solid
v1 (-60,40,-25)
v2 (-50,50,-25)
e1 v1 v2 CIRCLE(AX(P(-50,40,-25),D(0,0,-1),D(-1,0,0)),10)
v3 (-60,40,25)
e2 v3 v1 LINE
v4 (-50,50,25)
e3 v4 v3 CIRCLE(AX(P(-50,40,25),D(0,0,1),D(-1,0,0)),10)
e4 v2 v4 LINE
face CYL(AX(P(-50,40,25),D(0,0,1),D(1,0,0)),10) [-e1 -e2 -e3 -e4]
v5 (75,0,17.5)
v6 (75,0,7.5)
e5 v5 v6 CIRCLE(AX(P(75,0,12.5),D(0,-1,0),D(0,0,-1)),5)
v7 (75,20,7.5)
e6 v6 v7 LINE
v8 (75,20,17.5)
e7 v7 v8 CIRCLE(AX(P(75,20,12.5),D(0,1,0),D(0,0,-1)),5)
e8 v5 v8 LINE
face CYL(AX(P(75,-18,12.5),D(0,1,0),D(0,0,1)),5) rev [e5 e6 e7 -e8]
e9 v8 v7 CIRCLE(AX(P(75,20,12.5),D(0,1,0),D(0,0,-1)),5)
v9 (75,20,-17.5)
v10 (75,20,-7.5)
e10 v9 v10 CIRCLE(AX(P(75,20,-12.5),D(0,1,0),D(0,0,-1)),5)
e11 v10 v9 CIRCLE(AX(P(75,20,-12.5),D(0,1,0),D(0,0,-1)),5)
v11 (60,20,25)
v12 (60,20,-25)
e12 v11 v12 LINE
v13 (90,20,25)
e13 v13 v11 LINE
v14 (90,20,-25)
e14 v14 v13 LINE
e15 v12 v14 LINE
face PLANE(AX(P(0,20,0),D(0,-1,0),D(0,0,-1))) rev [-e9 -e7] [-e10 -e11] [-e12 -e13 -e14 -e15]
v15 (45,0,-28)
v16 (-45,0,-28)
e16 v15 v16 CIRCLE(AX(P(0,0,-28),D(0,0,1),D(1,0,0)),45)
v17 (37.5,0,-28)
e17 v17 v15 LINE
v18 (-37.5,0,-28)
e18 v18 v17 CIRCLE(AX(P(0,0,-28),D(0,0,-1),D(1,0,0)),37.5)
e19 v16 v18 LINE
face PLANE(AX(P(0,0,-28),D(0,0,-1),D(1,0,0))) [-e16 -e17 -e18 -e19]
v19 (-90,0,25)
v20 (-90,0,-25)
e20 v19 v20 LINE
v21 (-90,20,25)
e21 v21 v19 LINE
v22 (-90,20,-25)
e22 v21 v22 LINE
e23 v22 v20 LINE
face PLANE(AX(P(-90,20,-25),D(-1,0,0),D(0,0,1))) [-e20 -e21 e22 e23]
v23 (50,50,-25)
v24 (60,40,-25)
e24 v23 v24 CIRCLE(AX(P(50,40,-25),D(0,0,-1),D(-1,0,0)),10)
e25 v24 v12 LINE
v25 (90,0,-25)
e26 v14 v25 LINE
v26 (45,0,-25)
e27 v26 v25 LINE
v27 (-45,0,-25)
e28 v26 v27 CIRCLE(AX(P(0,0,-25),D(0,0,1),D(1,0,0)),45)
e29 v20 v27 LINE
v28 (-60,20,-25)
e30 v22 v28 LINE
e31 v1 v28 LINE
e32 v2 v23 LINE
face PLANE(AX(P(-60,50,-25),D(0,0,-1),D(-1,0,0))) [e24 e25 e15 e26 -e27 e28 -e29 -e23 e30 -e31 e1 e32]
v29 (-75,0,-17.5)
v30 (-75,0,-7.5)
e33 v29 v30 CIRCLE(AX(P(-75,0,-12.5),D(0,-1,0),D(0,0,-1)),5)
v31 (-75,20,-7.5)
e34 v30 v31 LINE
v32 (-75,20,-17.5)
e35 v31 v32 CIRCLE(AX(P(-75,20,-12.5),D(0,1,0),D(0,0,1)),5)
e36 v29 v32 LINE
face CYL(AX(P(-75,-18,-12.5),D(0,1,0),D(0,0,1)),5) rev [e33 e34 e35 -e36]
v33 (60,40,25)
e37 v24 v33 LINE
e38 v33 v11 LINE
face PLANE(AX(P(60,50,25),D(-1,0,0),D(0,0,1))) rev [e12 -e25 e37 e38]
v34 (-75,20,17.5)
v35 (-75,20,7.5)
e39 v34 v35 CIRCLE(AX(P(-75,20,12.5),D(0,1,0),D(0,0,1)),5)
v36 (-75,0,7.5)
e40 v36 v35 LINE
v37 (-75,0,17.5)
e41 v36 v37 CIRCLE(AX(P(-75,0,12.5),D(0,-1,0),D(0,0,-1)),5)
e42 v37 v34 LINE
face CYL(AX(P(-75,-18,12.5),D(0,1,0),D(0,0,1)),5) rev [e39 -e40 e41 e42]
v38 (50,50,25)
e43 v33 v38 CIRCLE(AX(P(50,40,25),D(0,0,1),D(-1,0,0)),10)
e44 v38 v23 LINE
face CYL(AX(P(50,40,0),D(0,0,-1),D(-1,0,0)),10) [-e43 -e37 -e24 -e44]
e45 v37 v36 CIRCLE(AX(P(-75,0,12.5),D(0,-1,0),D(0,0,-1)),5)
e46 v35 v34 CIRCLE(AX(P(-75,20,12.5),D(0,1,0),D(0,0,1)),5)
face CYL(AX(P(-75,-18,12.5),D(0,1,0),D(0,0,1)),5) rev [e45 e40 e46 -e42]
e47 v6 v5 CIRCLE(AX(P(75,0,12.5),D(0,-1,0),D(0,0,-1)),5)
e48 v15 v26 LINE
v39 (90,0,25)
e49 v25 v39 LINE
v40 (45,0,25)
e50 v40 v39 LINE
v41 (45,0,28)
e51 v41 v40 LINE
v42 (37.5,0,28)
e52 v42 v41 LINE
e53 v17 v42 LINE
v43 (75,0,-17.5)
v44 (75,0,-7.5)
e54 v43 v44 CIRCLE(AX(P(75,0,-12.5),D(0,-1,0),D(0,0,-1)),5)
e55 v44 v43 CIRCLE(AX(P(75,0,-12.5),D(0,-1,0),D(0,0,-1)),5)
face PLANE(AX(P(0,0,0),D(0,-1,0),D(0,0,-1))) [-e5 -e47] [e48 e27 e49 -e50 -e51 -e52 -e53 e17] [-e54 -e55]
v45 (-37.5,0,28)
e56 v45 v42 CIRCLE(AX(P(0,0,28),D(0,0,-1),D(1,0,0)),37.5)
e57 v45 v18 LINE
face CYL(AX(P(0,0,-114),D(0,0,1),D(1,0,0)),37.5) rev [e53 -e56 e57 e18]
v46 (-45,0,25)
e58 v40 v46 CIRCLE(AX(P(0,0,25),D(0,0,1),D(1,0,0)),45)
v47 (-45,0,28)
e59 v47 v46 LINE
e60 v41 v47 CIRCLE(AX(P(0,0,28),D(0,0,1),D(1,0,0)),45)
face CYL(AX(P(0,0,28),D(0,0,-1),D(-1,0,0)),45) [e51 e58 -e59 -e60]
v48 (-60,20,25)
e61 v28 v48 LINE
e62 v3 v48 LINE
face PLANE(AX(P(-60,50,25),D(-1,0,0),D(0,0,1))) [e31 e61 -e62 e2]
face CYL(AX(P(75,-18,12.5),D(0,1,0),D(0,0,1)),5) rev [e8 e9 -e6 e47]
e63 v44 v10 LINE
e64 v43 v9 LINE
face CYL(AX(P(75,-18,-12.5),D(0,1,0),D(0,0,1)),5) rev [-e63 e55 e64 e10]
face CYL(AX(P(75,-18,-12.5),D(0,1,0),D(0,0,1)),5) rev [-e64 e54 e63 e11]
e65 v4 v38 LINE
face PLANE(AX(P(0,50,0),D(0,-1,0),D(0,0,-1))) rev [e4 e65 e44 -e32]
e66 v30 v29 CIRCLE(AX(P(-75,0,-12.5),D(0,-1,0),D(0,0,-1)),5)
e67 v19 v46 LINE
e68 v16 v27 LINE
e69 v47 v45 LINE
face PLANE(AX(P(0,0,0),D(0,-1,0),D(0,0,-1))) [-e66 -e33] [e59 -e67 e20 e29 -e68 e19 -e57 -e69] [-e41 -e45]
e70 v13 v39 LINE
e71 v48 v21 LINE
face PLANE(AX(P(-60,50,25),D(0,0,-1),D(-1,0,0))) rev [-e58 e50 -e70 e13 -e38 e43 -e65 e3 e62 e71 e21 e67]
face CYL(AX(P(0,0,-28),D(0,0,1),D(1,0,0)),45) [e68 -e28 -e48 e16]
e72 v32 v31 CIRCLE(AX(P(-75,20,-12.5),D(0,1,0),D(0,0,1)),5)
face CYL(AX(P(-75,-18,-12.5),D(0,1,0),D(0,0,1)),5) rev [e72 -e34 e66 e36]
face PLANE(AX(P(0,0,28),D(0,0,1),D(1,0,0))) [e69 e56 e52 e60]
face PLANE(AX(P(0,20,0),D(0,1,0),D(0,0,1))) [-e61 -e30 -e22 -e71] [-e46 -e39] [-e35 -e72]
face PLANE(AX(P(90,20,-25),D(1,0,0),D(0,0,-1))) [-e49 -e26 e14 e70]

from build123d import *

# Parameters (mm, degrees)
SKETCH_2_W          = 120
SKETCH_2_H          = 50
EXTRUDE_1_DEPTH     = 50
SKETCH_3_R          = 37.5
CUT_EXTRUDE_1_DEPTH = 139
FILLET_1_R          = 10
SKETCH_4_W          = 30
SKETCH_4_H          = 50
EXTRUDE_2_DEPTH     = 20
EXTRUDE_START       = 3
EXTRUDE_3_DEPTH     = 3
SKETCH_6_R          = 5
CUT_EXTRUDE_2_DEPTH = 38


with BuildPart() as part:
    # 草图2 → 凸台-拉伸1 (new body)
    with BuildSketch(Plane(origin=(0, 0, 0), x_dir=(1, 0, 0), z_dir=(0, 1, 0))):
        Rectangle(SKETCH_2_W, SKETCH_2_H)
    extrude(amount=EXTRUDE_1_DEPTH)

    # 草图3 → 切除-拉伸1 (cut)
    with BuildSketch(Plane.XY.offset(25)):
        Circle(SKETCH_3_R)
    extrude(amount=-CUT_EXTRUDE_1_DEPTH, mode=Mode.SUBTRACT)

    # 圆角1
    fillet_1_edges = [part.edges().sort_by_distance(p)[0] for p in [
        (60, 50, 0),
        (-60, 50, 0),
    ]]
    fillet(fillet_1_edges, radius=FILLET_1_R)

    # 草图4 → 凸台-拉伸2 (add)
    with BuildSketch(Plane.XZ):
        with Locations((-75, 0)):
            Rectangle(SKETCH_4_W, SKETCH_4_H)
        with Locations((75, 0)):
            Rectangle(SKETCH_4_W, SKETCH_4_H)
    extrude(amount=-EXTRUDE_2_DEPTH)

    # 草图5 → 凸台-拉伸3 (add)
    with BuildSketch(Plane.XY.offset(25).offset(EXTRUDE_START)):
        with BuildLine():
            Line((-45, 0), (-37.5, 0))
            ThreePointArc((-37.5, 0), (0, 37.5), (37.5, 0))
            Line((37.5, 0), (45, 0))
            ThreePointArc((45, 0), (0, 45), (-45, 0))
        make_face()
    extrude_3 = extrude(amount=-EXTRUDE_3_DEPTH)

    # 镜向1: 凸台-拉伸3 across plane
    add(extrude_3.mirror(Plane.XY))

    # 草图6 → 切除-拉伸2 (cut)
    with BuildSketch(Plane(origin=(0, 20, 0), x_dir=(1, 0, 0), z_dir=(0, 1, 0))):
        with Locations(Location((-75, 12.5, 0), (0, 0, 270))):
            Circle(SKETCH_6_R)
        with Locations(Location((-75, -12.5, 0), (0, 0, 270))):
            Circle(SKETCH_6_R)
        with Locations(Location((75, -12.5, 0), (0, 0, 90))):
            Circle(SKETCH_6_R)
        with Locations(Location((75, 12.5, 0), (0, 0, 90))):
            Circle(SKETCH_6_R)
    extrude(amount=-CUT_EXTRUDE_2_DEPTH, mode=Mode.SUBTRACT)


solid = part.part
